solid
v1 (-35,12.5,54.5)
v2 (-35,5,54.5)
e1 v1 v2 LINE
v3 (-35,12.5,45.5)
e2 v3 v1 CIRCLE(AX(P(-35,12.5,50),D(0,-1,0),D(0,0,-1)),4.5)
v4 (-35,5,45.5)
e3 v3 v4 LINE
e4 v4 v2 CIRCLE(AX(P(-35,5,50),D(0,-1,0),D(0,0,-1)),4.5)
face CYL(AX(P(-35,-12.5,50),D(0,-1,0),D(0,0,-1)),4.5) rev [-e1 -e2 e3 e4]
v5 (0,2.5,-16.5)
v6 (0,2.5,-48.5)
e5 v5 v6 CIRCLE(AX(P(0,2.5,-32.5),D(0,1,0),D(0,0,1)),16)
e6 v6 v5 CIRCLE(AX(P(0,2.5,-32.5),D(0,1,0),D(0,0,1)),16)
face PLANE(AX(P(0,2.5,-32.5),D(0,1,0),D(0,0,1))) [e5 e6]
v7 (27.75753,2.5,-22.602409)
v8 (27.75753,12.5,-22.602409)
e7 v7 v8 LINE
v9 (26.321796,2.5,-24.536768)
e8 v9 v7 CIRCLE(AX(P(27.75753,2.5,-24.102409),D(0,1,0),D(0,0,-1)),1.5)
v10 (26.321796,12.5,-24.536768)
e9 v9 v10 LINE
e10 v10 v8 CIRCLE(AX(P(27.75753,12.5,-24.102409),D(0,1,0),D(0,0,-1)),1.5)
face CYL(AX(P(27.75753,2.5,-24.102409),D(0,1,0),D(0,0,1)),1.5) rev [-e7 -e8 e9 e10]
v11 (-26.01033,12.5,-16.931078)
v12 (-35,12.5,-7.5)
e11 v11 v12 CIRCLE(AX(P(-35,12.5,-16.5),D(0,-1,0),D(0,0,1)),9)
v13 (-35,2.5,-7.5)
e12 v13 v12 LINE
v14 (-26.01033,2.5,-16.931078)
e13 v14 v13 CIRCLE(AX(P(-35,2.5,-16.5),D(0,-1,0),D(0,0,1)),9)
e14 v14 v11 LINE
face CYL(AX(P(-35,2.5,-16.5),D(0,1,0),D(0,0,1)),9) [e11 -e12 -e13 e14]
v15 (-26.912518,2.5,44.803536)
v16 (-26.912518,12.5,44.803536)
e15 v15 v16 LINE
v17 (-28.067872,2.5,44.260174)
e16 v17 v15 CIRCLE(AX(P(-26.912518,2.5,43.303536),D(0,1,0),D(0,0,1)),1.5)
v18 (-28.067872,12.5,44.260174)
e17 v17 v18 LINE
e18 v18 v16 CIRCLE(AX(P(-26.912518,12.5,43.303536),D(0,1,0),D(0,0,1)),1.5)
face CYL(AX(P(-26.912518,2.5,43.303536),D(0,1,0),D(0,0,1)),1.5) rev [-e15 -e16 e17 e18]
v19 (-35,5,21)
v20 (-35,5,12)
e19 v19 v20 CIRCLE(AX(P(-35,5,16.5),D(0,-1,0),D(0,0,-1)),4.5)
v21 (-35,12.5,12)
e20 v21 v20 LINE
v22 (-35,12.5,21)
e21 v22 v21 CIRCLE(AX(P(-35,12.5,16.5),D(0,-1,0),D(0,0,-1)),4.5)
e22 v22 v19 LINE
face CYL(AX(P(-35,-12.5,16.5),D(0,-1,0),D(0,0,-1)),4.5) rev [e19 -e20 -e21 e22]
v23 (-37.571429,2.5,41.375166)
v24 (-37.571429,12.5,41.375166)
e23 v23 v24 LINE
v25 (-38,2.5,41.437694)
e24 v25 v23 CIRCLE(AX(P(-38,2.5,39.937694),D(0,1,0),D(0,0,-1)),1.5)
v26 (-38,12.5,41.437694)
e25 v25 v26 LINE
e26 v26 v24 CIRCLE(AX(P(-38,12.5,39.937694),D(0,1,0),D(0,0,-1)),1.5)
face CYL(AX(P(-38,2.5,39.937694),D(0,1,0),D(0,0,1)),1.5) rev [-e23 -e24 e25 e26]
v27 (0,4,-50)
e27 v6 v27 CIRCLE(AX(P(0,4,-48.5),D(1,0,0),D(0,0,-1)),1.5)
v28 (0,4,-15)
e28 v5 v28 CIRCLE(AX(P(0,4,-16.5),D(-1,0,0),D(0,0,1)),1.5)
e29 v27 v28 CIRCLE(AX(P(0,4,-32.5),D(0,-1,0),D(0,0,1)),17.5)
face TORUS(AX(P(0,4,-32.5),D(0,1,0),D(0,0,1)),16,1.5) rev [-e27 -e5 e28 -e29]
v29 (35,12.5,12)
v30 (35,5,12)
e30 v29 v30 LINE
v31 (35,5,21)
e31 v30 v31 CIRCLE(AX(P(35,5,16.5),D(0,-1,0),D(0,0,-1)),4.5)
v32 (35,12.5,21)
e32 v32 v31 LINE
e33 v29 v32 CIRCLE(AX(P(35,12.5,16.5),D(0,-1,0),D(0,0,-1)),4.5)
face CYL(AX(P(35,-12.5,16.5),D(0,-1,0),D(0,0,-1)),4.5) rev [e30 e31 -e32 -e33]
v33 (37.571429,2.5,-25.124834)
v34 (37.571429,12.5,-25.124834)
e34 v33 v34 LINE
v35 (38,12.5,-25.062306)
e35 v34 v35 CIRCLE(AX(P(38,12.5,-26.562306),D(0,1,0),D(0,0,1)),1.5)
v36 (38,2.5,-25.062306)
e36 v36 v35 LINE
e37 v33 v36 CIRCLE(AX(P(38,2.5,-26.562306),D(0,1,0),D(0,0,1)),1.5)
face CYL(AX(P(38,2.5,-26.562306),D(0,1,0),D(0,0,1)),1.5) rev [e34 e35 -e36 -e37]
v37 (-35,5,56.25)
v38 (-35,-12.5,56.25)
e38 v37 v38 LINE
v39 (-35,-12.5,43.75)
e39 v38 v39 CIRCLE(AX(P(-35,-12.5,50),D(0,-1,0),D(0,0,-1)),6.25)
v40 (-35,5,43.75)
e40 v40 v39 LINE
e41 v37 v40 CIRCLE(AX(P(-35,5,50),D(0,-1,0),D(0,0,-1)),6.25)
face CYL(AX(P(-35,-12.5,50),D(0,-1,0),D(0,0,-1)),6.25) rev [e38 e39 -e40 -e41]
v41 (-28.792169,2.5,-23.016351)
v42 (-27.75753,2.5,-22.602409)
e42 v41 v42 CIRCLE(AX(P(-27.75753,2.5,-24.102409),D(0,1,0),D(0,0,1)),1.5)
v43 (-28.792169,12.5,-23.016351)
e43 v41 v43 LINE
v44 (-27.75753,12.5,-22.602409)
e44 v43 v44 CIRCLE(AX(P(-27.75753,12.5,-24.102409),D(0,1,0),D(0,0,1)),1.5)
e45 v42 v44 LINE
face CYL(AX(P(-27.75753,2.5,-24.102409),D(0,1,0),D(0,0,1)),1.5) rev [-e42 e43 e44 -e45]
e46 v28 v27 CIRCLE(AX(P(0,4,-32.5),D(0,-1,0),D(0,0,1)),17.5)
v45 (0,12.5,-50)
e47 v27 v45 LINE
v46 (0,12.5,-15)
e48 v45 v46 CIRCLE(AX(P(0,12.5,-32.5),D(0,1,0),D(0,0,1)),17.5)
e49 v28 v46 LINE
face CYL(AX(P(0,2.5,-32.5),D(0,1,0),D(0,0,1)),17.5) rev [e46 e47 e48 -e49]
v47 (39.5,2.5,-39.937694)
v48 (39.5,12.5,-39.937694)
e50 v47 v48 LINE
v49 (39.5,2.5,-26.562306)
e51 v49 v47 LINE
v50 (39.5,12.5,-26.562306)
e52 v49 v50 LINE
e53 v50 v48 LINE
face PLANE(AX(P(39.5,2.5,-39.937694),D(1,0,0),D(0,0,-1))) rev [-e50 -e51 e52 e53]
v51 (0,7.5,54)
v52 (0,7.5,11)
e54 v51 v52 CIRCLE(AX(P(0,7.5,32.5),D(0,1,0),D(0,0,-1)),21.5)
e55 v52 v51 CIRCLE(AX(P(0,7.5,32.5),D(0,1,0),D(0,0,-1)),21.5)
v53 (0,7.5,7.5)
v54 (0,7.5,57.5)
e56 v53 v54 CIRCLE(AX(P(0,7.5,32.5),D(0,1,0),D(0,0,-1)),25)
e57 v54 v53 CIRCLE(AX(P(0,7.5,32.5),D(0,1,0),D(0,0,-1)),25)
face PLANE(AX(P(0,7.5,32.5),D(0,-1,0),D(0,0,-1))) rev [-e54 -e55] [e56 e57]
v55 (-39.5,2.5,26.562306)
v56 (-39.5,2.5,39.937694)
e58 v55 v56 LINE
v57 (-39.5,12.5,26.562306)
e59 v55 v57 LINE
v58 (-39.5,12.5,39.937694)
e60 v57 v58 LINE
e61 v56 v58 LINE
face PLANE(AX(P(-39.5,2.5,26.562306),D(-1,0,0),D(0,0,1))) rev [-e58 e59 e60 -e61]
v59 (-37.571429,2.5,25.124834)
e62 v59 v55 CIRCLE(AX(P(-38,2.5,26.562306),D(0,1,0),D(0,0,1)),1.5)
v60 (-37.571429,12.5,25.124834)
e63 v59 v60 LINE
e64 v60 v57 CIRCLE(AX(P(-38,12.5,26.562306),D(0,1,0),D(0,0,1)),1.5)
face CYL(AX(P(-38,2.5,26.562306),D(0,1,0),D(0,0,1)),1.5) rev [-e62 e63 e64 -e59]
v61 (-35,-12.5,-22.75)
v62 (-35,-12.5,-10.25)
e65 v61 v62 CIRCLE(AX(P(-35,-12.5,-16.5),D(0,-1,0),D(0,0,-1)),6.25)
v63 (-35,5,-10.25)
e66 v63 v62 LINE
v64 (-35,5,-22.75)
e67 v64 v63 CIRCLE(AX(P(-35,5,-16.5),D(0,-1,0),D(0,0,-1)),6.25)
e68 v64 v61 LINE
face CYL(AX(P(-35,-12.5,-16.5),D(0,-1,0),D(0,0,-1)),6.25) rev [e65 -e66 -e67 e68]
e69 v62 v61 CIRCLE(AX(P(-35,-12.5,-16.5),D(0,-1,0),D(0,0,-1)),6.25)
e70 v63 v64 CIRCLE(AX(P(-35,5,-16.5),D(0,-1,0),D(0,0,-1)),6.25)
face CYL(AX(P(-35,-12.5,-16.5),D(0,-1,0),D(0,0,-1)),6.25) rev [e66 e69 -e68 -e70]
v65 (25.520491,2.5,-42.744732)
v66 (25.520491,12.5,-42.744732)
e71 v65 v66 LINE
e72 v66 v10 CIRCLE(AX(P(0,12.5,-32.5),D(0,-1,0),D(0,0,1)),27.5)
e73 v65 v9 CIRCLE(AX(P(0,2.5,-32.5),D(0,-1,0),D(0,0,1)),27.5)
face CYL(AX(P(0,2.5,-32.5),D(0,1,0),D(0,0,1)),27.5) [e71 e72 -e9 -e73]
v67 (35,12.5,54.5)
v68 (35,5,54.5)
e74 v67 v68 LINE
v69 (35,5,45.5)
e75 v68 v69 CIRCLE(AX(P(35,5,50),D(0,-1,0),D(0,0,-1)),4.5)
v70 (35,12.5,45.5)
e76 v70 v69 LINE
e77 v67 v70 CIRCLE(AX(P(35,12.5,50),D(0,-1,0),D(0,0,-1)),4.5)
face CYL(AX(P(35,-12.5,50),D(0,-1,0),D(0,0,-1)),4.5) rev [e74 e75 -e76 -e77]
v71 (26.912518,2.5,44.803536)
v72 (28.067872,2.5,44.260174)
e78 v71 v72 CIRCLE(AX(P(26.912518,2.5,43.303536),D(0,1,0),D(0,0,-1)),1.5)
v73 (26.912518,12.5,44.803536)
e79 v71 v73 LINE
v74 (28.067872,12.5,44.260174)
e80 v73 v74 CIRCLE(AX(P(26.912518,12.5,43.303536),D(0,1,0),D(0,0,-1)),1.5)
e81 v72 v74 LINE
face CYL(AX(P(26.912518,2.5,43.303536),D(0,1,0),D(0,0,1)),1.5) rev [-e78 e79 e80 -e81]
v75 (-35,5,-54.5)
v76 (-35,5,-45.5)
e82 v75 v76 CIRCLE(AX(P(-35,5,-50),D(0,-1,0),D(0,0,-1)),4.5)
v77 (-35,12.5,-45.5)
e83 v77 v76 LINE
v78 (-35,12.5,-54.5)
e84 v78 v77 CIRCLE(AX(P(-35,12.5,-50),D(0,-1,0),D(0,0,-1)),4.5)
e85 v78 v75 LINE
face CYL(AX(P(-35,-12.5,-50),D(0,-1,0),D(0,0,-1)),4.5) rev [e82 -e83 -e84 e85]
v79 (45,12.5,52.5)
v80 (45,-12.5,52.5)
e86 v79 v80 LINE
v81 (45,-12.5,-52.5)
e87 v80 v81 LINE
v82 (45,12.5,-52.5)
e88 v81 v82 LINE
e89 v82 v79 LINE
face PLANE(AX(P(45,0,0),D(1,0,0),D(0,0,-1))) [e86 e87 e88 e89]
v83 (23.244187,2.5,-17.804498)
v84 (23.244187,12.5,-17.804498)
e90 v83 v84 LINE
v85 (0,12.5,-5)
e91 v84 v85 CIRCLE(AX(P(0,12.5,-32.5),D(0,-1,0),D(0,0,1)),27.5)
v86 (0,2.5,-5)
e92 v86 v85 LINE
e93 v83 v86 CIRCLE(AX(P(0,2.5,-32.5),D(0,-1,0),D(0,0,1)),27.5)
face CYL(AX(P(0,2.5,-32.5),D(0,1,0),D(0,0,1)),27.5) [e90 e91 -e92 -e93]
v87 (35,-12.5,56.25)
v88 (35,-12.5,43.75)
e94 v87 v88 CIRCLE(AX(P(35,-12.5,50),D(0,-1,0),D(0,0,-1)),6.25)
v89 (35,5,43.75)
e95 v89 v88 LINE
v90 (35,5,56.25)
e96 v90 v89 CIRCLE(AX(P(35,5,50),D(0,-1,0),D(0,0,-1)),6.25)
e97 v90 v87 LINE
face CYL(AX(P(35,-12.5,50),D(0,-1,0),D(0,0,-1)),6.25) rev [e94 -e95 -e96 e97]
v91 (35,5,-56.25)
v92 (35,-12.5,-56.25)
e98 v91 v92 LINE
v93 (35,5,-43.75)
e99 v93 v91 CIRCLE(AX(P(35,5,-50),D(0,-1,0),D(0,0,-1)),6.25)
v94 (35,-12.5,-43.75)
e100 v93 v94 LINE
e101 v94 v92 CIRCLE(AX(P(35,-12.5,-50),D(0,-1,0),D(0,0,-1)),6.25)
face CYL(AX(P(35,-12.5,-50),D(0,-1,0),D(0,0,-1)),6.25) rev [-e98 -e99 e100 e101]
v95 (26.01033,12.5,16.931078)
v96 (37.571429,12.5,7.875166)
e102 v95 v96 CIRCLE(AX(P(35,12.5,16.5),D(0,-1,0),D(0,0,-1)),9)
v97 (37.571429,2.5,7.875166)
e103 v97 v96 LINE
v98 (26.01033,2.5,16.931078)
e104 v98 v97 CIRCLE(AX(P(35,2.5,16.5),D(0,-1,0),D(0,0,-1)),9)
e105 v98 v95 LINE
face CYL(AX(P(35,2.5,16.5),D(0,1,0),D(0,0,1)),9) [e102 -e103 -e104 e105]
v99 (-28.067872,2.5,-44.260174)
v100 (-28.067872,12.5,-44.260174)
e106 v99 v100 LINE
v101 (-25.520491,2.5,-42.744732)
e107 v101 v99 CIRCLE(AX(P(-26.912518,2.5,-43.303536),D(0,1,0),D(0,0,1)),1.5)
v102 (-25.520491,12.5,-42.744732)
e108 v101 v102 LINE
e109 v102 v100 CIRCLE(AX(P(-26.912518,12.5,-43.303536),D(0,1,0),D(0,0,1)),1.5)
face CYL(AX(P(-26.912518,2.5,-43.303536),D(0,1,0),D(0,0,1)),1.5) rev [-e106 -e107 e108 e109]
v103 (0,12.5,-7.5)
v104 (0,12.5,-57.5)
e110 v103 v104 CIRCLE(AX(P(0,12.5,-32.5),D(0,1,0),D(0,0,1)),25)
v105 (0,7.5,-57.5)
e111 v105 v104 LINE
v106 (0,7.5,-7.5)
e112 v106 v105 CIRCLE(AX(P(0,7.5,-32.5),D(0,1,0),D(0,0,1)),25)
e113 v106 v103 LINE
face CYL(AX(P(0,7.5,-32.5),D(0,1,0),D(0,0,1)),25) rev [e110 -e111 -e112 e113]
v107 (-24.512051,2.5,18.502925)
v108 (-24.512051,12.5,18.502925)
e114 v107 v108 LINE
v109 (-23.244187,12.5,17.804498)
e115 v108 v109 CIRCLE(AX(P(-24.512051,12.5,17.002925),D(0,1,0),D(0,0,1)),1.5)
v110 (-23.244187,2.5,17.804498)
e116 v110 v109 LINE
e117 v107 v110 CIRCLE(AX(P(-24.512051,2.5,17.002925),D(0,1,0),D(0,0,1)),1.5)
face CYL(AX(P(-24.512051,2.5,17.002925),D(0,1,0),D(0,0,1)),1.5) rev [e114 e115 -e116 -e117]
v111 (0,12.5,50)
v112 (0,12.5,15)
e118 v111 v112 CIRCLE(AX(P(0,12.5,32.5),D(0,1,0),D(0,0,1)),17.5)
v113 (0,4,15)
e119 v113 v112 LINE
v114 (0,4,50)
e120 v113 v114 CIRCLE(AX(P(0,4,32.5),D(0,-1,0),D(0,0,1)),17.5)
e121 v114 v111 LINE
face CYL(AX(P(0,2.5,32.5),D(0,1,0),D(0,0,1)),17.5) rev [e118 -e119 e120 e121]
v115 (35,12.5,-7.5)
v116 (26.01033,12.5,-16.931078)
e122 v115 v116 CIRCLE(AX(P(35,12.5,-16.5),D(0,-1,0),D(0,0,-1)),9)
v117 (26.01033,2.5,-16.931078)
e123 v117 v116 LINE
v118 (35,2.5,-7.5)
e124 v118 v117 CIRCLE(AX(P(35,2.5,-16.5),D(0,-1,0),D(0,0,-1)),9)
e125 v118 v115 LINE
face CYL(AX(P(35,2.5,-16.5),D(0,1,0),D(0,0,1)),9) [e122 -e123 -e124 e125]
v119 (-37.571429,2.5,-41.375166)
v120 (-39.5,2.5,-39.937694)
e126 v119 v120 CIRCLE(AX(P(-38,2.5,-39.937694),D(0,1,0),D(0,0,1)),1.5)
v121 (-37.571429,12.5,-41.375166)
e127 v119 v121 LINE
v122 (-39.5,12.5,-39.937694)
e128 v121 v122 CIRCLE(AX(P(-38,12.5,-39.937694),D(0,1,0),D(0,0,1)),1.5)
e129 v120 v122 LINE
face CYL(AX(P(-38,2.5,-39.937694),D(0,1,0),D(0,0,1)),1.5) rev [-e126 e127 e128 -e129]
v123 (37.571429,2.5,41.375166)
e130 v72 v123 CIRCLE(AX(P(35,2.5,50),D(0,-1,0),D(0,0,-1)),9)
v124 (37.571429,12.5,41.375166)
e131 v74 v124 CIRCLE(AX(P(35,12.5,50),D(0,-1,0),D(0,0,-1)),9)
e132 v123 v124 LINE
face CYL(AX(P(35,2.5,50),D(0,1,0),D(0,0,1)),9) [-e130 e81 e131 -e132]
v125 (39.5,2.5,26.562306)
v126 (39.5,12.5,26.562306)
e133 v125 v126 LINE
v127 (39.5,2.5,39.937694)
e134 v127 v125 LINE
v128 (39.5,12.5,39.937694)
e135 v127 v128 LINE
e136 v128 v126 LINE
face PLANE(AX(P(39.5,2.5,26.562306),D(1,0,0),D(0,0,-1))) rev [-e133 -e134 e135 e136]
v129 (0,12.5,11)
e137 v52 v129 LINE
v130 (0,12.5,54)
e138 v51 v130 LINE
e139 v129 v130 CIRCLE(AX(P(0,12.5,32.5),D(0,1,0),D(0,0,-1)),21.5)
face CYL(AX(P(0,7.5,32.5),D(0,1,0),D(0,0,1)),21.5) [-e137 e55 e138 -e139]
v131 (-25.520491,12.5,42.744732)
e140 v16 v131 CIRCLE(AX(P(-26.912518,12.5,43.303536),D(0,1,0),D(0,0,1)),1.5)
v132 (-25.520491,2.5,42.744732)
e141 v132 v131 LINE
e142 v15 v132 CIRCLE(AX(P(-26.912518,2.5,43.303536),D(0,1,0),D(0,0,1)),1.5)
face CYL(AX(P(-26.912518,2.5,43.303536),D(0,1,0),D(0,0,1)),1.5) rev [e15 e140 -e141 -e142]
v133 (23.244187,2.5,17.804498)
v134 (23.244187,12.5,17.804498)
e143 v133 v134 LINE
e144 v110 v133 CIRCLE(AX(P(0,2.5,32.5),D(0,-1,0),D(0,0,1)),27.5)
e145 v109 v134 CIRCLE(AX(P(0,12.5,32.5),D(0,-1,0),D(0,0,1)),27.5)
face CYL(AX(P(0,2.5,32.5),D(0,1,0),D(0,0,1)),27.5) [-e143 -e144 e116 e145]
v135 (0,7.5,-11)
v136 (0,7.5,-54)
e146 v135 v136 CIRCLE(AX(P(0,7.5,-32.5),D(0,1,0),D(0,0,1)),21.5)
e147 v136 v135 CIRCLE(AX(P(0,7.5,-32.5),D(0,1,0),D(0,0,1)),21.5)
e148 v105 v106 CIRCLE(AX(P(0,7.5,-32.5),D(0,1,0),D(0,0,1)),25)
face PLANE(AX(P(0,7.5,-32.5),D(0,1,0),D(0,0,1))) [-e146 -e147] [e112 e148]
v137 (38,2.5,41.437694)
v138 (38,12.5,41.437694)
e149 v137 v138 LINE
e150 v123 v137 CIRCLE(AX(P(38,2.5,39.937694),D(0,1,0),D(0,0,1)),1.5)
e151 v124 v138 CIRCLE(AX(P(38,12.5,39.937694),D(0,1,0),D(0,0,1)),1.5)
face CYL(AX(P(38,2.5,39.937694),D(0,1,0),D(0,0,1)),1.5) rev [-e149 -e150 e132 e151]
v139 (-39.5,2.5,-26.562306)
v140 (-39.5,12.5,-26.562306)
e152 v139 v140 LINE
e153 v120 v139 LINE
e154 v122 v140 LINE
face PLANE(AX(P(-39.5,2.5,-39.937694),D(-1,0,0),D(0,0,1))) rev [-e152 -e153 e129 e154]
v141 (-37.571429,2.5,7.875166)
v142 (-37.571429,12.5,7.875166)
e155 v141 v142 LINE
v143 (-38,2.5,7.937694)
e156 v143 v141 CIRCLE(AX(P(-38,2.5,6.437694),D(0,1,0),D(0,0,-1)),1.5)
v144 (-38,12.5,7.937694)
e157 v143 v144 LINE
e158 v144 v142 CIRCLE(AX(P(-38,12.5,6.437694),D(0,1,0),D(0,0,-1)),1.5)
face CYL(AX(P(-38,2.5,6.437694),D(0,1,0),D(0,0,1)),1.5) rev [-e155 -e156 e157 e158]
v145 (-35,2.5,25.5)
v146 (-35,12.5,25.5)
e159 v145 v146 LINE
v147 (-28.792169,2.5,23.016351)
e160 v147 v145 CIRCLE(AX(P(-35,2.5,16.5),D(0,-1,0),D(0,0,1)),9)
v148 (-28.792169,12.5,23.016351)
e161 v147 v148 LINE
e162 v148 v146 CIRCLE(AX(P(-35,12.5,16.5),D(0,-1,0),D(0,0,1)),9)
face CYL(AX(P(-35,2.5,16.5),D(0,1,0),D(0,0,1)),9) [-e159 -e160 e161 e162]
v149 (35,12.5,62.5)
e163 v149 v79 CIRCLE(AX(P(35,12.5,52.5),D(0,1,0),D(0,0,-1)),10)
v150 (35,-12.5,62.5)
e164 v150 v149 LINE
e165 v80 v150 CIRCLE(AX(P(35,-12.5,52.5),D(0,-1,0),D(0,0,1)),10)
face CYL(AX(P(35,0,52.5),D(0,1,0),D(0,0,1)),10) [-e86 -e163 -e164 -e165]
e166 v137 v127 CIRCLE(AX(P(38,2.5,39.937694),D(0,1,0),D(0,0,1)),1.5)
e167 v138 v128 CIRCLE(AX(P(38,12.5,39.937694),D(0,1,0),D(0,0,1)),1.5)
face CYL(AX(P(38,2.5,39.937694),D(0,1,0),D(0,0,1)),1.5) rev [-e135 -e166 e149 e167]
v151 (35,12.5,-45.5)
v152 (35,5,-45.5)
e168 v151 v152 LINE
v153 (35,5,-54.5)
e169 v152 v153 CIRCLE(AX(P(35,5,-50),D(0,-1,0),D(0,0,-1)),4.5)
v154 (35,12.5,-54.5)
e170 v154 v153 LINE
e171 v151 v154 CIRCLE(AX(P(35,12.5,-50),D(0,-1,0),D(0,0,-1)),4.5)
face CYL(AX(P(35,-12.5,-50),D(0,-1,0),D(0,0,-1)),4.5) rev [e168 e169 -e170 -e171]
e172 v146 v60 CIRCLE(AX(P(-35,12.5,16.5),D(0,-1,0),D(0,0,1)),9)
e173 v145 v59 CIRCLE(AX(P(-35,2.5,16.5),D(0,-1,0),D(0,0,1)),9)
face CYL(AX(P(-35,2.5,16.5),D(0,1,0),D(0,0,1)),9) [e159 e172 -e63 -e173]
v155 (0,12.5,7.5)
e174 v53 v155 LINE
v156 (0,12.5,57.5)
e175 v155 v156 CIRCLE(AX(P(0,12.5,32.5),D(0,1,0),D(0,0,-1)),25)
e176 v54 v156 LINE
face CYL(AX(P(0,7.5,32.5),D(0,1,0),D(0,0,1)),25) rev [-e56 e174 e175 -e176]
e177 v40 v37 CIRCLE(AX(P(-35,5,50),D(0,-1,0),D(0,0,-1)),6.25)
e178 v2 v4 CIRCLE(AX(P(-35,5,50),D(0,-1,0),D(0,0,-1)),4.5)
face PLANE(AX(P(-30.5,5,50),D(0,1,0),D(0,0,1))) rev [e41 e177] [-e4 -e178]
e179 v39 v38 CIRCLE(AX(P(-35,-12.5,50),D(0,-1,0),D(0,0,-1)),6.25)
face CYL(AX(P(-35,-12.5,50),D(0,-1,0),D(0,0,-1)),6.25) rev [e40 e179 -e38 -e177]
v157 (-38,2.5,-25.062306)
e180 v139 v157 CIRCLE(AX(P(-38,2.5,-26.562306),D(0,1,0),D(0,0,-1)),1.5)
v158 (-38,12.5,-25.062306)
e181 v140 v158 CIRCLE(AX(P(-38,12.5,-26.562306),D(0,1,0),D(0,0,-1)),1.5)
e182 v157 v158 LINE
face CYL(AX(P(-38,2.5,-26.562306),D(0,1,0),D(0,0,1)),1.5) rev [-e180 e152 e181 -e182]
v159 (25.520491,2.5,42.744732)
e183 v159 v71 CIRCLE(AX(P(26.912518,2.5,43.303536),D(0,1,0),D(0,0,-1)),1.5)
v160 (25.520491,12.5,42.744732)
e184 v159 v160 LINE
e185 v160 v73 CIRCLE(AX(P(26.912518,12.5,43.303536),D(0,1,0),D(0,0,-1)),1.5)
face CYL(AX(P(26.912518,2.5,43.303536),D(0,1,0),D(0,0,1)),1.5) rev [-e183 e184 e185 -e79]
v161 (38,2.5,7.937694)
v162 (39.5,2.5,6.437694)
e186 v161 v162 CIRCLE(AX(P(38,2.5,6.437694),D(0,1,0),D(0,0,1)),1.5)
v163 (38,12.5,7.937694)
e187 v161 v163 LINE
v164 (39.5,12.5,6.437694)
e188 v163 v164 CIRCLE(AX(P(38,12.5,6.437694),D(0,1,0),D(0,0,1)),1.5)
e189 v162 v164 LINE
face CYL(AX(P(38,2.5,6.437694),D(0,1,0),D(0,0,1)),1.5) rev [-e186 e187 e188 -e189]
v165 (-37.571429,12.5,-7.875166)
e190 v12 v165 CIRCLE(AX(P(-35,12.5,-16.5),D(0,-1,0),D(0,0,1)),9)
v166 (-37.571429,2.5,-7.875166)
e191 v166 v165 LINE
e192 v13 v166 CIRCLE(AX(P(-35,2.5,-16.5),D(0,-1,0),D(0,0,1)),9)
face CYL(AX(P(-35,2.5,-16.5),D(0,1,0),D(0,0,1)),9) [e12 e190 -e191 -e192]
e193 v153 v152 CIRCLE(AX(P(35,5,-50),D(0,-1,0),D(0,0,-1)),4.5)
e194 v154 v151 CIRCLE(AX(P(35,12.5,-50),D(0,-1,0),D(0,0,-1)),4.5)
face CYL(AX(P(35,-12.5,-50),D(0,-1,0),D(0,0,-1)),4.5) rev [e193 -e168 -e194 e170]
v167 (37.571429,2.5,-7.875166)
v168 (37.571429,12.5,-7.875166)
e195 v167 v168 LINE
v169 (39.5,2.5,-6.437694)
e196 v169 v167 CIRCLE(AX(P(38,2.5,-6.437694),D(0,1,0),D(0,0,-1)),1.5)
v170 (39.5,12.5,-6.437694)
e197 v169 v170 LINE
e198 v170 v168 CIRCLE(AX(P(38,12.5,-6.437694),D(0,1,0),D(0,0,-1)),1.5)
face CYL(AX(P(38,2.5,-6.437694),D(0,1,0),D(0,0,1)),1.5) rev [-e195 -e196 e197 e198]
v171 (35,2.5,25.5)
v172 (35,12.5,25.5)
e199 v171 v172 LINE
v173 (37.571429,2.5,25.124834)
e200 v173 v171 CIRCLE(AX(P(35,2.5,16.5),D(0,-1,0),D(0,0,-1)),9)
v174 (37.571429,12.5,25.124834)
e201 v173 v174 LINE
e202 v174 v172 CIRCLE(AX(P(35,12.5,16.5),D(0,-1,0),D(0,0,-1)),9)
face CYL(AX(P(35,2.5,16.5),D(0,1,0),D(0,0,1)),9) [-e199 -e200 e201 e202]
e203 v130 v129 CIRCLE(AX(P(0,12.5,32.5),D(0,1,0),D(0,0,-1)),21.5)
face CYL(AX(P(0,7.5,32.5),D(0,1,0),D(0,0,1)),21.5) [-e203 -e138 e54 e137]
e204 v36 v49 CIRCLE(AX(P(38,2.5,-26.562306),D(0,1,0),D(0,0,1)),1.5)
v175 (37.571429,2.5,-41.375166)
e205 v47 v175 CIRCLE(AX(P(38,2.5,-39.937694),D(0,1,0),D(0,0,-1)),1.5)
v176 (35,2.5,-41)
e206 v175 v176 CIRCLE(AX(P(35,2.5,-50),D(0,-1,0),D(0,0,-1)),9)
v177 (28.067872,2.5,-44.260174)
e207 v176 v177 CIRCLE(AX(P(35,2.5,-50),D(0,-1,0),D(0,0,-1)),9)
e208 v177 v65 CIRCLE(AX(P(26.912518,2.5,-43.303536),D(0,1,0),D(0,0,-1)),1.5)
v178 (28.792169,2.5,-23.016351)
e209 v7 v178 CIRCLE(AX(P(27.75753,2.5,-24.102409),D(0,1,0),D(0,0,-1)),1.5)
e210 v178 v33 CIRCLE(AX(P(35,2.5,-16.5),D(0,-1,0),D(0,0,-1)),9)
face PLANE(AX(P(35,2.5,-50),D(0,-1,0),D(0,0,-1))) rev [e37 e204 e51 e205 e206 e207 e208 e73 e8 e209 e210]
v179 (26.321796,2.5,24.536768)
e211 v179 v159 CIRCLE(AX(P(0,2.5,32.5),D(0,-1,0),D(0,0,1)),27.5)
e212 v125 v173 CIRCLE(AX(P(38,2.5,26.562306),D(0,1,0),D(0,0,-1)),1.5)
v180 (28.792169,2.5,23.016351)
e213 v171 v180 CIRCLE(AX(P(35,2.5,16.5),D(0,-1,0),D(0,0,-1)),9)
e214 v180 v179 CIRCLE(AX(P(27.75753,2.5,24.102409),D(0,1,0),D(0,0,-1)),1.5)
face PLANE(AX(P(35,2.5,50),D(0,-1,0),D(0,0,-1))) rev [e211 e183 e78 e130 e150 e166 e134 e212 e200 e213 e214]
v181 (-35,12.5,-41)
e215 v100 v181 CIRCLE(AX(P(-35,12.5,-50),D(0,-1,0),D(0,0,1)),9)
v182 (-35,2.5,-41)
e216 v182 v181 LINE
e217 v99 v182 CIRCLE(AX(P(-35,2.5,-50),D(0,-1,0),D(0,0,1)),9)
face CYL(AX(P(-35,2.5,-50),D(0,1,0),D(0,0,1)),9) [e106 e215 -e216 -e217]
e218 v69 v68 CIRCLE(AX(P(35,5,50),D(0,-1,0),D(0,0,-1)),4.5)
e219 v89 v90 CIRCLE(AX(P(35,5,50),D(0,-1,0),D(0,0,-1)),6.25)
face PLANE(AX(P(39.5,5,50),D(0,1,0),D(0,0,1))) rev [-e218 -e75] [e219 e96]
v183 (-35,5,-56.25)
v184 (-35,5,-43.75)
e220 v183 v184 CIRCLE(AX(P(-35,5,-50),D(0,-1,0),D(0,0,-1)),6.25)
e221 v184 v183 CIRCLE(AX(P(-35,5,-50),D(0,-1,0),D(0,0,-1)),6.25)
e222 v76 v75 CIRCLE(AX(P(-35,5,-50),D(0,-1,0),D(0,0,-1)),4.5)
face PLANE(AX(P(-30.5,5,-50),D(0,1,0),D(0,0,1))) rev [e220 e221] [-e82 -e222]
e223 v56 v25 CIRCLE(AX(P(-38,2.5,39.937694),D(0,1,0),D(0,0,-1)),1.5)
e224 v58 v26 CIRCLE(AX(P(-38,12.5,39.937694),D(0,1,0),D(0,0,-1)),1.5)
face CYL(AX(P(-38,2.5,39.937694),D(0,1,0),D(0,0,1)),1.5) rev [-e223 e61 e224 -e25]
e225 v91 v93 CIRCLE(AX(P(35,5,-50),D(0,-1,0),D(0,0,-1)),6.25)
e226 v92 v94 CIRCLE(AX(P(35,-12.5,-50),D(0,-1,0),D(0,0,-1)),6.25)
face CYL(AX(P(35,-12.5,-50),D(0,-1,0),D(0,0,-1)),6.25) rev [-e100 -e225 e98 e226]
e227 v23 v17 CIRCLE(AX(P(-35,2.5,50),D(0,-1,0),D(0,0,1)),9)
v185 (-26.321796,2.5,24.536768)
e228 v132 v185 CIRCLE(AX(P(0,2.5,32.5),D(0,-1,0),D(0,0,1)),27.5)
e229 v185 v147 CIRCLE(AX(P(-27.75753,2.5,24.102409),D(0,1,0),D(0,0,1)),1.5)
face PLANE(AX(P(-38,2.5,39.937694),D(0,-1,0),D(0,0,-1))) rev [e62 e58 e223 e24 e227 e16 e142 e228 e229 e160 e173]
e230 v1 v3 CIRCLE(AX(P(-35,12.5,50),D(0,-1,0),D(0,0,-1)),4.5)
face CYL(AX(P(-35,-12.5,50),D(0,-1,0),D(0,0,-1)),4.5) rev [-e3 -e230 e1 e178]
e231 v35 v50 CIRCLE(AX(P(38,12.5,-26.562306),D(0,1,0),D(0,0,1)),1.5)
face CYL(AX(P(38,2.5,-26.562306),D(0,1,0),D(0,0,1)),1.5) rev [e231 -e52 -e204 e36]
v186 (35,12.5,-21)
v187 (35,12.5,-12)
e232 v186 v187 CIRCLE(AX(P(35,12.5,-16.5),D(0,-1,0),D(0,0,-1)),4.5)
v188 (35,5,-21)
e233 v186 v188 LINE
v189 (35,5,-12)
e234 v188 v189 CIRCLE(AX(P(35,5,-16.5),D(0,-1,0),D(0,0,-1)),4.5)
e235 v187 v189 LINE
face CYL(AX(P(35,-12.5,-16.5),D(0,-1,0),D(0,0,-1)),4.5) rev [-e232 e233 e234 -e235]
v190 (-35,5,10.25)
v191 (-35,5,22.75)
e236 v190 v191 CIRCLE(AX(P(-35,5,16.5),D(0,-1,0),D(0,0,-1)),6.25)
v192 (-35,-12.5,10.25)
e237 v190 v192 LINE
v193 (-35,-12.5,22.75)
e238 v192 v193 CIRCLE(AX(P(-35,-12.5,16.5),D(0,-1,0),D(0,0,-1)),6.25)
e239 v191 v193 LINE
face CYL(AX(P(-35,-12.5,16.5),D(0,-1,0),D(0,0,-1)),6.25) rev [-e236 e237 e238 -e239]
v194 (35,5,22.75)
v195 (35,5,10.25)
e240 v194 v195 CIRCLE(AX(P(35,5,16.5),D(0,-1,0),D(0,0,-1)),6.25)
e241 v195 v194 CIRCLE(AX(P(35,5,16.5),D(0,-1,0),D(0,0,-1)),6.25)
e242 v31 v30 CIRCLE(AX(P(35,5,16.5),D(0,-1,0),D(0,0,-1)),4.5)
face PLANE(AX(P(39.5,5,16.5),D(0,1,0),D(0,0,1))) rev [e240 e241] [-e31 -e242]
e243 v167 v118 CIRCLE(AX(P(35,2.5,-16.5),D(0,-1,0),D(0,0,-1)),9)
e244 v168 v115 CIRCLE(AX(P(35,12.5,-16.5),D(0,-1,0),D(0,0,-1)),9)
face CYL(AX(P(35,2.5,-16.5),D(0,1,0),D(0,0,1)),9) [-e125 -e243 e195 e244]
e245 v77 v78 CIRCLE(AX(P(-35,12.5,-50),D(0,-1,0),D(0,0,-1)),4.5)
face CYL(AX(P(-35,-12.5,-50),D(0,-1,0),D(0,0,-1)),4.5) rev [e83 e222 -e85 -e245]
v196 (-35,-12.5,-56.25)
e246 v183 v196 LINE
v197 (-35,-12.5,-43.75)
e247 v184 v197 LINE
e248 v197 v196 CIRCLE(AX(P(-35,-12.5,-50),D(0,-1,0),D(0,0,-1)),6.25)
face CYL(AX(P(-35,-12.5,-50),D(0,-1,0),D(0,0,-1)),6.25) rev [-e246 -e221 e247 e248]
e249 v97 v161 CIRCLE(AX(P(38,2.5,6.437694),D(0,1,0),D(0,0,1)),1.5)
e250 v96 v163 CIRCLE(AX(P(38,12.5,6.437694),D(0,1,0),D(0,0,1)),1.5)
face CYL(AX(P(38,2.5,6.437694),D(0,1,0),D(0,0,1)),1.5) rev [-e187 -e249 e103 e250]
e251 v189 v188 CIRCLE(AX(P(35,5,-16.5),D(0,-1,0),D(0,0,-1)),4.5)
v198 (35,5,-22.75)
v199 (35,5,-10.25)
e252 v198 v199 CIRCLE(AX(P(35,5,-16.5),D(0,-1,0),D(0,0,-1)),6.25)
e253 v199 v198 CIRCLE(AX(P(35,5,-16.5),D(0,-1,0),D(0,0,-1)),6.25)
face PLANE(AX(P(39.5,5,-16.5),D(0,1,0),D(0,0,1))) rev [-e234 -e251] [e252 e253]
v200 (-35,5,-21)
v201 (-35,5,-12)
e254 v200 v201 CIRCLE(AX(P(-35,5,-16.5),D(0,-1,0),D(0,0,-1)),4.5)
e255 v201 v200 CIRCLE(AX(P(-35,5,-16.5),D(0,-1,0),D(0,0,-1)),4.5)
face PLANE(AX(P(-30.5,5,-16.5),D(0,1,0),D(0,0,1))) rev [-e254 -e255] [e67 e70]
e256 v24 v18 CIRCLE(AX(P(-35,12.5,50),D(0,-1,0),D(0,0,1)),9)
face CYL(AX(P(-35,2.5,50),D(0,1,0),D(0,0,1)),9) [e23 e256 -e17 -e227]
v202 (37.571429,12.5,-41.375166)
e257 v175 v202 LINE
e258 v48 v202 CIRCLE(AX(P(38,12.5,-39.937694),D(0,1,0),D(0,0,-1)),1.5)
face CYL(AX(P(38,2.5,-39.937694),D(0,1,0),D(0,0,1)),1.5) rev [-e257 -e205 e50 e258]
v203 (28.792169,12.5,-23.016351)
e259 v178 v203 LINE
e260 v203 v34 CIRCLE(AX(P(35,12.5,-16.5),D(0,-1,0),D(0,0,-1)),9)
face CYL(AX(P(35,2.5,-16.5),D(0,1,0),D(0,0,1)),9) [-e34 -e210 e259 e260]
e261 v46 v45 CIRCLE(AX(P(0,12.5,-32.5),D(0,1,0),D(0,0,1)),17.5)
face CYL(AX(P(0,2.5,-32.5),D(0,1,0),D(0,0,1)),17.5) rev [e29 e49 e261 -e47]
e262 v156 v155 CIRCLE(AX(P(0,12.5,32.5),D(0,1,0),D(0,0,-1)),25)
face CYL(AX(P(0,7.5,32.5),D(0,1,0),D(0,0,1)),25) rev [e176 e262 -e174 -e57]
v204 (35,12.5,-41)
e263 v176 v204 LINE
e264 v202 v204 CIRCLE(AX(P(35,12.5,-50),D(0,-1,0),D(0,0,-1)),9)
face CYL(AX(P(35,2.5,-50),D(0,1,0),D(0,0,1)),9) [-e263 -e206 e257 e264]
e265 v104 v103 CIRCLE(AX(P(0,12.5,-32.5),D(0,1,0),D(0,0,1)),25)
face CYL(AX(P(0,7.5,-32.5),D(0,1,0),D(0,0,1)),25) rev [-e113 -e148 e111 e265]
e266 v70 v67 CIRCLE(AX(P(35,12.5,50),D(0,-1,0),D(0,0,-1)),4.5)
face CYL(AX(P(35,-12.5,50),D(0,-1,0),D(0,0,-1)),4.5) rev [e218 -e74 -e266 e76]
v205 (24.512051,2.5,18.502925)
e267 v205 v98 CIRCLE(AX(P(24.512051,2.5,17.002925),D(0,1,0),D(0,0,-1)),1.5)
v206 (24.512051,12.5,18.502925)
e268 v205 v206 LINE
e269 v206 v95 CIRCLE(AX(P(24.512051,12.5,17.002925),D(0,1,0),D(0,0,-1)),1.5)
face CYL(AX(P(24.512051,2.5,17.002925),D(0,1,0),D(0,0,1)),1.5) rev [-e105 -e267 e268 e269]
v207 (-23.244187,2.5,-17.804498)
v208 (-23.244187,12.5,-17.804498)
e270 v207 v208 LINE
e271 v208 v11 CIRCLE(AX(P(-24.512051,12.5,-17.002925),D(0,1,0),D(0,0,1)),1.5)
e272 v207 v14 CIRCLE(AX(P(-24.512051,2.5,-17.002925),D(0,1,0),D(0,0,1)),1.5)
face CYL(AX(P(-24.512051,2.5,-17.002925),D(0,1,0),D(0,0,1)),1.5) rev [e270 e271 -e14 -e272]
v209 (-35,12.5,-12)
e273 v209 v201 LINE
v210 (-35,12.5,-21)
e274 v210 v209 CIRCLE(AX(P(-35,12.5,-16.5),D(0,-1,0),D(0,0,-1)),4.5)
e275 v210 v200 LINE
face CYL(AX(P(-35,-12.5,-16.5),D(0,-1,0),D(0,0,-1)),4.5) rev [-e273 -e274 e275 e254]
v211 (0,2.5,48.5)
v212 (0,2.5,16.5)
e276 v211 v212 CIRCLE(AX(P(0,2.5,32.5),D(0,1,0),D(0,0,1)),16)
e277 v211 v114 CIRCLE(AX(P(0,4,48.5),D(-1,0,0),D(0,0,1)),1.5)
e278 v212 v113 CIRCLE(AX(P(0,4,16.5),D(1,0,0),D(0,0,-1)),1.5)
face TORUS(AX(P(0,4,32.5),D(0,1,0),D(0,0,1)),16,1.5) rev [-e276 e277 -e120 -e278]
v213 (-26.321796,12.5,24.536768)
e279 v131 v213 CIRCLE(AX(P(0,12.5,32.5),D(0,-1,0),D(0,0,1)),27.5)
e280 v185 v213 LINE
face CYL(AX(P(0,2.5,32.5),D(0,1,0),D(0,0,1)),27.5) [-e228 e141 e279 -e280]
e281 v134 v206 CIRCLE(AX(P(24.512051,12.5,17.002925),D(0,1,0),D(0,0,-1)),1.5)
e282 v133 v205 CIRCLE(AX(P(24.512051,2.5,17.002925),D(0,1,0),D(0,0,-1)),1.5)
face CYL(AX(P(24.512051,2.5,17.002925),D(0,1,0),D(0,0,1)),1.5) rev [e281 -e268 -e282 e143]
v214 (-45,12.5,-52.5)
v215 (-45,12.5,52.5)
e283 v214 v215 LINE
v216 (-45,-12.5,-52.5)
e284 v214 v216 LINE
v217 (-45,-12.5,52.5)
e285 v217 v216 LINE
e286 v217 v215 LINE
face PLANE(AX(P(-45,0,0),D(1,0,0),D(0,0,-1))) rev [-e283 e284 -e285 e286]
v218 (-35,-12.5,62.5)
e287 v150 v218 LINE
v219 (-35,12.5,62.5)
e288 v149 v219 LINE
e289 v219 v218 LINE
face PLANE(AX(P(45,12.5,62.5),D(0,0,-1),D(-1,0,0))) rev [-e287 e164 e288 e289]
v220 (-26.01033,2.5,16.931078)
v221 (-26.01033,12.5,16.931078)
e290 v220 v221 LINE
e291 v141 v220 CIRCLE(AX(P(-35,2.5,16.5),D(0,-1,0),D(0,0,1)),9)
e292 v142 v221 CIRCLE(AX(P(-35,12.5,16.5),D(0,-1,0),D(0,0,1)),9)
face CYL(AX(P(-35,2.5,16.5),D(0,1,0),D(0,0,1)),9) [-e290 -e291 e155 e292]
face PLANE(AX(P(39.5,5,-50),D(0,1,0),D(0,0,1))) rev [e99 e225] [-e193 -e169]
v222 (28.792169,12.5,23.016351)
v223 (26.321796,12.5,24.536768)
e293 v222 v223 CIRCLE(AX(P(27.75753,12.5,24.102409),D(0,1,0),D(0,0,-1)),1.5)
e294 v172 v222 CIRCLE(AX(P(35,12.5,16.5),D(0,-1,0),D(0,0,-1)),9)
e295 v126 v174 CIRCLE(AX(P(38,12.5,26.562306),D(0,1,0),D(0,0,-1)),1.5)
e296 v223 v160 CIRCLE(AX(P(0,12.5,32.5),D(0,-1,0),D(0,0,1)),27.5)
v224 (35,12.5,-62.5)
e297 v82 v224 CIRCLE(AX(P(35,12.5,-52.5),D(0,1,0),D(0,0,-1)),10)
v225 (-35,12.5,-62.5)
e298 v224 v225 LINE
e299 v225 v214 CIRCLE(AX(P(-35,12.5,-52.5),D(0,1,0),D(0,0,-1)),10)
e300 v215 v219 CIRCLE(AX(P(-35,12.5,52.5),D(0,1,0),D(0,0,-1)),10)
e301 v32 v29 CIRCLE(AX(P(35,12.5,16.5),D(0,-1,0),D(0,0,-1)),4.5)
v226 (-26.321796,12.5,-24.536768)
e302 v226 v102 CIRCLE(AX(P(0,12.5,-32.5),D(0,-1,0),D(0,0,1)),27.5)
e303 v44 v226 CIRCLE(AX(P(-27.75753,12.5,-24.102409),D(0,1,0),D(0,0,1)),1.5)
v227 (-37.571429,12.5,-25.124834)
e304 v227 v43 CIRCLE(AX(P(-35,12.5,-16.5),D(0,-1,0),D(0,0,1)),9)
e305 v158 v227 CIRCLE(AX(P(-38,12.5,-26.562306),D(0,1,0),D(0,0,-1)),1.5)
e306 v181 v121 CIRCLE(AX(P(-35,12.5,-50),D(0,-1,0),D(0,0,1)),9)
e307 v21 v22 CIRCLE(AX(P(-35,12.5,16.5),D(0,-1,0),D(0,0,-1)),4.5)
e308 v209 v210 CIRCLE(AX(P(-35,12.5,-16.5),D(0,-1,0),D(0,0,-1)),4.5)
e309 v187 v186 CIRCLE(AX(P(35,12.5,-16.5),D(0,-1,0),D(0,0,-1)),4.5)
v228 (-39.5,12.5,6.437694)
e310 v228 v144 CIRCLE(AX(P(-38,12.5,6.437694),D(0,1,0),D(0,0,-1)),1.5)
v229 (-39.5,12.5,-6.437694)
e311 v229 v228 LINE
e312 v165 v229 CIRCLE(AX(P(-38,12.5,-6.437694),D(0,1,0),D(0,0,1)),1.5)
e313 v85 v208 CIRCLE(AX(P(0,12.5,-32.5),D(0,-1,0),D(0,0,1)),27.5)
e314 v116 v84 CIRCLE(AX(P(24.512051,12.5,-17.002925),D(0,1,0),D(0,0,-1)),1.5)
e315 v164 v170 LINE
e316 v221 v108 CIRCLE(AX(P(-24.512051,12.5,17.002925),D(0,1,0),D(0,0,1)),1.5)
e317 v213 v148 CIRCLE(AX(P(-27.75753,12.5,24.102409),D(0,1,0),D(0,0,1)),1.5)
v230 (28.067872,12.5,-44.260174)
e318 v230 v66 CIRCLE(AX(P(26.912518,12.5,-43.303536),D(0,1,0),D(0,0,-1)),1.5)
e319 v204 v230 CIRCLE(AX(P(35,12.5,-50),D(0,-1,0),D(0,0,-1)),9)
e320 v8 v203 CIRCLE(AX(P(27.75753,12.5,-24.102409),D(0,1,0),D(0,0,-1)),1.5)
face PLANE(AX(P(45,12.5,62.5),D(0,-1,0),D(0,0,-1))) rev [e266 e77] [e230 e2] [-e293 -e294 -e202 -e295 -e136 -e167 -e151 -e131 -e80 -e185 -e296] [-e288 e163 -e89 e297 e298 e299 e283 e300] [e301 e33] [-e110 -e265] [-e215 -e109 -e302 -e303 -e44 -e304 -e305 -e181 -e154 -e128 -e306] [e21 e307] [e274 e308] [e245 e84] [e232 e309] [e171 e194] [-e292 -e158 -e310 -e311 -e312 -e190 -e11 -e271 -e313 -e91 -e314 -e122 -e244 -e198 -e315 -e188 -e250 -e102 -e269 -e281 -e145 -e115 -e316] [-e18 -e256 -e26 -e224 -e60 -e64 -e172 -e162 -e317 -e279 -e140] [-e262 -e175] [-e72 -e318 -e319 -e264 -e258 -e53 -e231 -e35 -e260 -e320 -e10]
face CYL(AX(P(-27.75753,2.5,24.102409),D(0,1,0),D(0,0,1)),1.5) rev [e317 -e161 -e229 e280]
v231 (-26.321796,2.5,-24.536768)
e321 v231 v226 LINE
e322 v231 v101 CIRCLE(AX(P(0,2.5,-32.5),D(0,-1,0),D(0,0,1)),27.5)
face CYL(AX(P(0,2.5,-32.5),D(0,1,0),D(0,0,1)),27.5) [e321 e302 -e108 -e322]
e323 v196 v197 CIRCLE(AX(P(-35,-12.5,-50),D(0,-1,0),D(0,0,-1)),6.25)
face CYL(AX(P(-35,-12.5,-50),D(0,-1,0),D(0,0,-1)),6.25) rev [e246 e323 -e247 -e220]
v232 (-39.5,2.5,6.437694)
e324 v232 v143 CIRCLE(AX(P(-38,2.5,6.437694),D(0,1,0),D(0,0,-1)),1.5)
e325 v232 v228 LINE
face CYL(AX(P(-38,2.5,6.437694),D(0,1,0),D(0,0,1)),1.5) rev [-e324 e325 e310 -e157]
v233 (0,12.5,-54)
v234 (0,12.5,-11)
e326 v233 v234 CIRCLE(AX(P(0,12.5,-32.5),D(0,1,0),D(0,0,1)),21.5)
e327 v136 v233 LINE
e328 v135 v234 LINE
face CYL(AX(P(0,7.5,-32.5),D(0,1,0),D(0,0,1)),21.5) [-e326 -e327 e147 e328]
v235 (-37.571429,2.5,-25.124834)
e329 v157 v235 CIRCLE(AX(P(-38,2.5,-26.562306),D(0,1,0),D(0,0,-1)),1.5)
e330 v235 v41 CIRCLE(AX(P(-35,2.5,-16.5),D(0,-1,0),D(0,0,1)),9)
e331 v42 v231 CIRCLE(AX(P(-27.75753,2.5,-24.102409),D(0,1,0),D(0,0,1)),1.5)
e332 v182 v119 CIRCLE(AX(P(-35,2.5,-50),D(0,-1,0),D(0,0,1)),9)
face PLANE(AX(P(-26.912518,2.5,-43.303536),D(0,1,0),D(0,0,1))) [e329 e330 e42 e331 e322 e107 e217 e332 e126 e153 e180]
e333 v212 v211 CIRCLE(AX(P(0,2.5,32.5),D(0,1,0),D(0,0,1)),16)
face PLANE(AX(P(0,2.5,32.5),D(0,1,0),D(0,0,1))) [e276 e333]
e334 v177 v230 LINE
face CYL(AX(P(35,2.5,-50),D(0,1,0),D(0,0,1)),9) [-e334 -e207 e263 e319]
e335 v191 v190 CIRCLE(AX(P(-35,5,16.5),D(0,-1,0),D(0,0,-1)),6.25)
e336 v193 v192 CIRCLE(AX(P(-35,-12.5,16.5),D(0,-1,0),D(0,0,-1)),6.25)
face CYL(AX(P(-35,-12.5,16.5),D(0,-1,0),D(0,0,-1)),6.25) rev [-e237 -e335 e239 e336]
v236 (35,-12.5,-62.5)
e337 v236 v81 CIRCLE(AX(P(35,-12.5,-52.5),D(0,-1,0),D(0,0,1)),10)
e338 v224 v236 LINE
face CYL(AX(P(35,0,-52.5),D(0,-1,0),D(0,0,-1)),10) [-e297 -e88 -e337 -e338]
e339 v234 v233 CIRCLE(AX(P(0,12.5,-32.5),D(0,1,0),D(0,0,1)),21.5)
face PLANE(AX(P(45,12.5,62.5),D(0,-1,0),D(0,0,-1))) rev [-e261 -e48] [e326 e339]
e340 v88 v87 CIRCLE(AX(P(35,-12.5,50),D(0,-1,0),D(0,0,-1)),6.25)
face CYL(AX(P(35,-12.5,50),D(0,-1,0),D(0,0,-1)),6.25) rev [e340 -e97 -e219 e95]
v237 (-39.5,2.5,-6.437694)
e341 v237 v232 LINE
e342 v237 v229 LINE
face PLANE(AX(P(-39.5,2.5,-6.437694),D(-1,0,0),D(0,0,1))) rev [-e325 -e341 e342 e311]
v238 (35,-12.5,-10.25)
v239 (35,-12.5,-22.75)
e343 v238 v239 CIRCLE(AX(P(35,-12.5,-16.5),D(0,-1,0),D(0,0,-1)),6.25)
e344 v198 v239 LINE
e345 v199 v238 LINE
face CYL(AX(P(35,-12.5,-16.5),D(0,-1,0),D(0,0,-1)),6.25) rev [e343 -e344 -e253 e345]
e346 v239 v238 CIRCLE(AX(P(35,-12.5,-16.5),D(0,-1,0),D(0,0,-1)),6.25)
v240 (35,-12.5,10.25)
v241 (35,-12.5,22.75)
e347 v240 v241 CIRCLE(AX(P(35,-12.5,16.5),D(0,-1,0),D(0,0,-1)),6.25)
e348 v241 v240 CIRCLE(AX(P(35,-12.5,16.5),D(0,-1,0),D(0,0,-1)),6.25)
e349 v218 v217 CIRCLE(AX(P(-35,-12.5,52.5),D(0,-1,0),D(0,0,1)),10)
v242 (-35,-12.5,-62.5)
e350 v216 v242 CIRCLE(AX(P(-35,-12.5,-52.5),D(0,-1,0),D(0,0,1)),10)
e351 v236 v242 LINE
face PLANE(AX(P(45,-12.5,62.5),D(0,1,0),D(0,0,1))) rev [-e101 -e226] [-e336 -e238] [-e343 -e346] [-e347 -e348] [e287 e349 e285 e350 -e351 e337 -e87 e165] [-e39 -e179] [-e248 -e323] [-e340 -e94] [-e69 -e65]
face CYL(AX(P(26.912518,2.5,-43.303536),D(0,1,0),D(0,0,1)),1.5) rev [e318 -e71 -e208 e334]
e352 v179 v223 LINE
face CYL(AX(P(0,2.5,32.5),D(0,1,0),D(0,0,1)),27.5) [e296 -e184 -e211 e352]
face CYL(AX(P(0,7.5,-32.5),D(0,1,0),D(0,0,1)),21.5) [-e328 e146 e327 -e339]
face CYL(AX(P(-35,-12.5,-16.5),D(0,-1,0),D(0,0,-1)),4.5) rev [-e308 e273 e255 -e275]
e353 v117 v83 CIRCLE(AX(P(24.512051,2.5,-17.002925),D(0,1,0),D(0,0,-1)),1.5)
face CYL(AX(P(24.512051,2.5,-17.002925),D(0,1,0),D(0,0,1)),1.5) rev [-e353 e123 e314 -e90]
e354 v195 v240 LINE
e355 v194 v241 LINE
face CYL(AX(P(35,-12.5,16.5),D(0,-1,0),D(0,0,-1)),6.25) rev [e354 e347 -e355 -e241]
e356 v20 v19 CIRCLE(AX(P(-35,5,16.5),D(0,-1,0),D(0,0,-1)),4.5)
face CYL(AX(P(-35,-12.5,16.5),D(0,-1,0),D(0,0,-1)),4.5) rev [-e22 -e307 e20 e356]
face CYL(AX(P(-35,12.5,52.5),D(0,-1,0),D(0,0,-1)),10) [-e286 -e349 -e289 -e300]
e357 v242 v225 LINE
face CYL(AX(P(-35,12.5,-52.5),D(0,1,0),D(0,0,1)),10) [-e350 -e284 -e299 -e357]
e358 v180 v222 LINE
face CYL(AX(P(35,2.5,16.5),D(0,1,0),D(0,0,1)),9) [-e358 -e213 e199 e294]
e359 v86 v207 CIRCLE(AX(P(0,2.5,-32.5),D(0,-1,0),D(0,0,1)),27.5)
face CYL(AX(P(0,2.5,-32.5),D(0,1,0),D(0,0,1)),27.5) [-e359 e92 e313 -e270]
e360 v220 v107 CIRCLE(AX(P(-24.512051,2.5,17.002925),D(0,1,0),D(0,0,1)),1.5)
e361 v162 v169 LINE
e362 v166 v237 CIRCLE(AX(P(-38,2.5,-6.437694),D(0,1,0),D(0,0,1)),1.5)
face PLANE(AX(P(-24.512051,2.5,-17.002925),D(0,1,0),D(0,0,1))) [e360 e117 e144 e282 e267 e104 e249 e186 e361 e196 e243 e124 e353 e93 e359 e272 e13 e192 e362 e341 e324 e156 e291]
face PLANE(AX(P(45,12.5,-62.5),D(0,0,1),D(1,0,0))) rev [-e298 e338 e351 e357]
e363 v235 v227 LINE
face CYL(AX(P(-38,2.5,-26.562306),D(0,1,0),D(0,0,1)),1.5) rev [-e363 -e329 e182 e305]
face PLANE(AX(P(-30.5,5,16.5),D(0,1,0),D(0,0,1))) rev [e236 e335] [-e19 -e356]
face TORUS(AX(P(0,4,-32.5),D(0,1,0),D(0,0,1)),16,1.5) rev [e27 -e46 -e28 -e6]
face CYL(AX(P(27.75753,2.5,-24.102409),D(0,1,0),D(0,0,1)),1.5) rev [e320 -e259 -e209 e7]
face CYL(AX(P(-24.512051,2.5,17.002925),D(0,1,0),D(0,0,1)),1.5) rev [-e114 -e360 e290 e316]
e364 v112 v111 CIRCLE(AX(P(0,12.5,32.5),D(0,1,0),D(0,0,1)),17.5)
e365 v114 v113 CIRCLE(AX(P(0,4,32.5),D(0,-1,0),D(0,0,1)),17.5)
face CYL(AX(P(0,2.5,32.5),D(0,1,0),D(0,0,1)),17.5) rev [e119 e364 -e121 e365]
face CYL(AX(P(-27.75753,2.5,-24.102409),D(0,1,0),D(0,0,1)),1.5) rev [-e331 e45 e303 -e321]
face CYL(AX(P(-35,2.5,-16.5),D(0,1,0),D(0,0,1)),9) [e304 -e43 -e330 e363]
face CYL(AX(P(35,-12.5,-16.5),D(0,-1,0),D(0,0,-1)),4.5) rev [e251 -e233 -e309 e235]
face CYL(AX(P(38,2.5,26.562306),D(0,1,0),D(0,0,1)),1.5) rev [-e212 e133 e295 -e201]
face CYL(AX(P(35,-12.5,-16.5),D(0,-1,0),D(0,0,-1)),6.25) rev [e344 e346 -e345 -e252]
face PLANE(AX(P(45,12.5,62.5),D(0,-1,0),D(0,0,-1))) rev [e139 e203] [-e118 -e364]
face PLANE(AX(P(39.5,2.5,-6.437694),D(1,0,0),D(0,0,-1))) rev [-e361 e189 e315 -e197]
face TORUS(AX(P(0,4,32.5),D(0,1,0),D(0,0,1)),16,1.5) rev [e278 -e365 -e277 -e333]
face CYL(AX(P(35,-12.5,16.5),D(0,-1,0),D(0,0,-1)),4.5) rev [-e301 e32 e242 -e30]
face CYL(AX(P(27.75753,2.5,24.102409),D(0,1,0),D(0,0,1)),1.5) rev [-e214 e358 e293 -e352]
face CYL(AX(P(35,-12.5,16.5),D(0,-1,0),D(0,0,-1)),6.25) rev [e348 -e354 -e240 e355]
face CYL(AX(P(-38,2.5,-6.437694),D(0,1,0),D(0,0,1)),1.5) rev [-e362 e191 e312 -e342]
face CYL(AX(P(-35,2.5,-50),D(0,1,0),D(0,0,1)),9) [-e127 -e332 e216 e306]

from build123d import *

# Parameters (mm, degrees)
BLOCK_PROFILE_SKETCH_W         = 125
BLOCK_PROFILE_SKETCH_H         = 25
BASE_BLOCK_DEPTH               = 45
BORE_RECESS_SKETCH_R           = 25
BORE_RECESS_SKETCH_R_2         = 21.5
BORE_RECESS_5MM_DEPTH          = 5
TWIN_BORE_SKETCH_R             = 17.5
TWIN_BORES_DEPTH               = 10
BORE_EDGE_FILLET_R1_5_R        = 1.5
RELIEF_POCKETS_DEPTH           = 10
BOLT_HOLES_CBORE_9_D           = 9
BOLT_HOLES_CBORE_9_DEPTH       = 100
BOLT_HOLES_CBORE_9_CBORE_D     = 12.5
BOLT_HOLES_CBORE_9_CBORE_DEPTH = 17.5
CORNER_FILLETS_R10_R           = 10


with BuildPart() as part:
    # Block Profile Sketch → Base Block (new, symmetric)
    with BuildSketch(Plane(origin=(0, 0, 0), x_dir=(0, 0, -1), z_dir=(1, 0, 0))):
        Rectangle(BLOCK_PROFILE_SKETCH_W, BLOCK_PROFILE_SKETCH_H)
    extrude(amount=BASE_BLOCK_DEPTH, both=True)

    # Bore Recess Sketch → Bore Recess 5mm (cut)
    # profile 1 of 2: a face of its own
    with BuildSketch(Plane(origin=(0, 12.5, 0), x_dir=(1, 0, 0), z_dir=(0, 1, 0))):
        with Locations(Location((0, 32.5, 0), (0, 0, 270))):
            Circle(BORE_RECESS_SKETCH_R)
        with Locations(Location((0, 32.5, 0), (0, 0, 270))):
            Circle(BORE_RECESS_SKETCH_R_2, mode=Mode.SUBTRACT)
    # profile 2 of 2: a face of its own
    with BuildSketch(Plane(origin=(0, 12.5, 0), x_dir=(1, 0, 0), z_dir=(0, 1, 0))):
        with Locations(Location((0, -32.5, 0), (0, 0, 90))):
            Circle(BORE_RECESS_SKETCH_R)
        with Locations(Location((0, -32.5, 0), (0, 0, 90))):
            Circle(BORE_RECESS_SKETCH_R_2, mode=Mode.SUBTRACT)
    extrude(amount=-BORE_RECESS_5MM_DEPTH, mode=Mode.SUBTRACT)

    # Twin Bore Sketch → Twin Bores (cut)
    with BuildSketch(Plane(origin=(0, 12.5, 0), x_dir=(1, 0, 0), z_dir=(0, 1, 0))):
        with Locations(Location((0, 32.5, 0), (0, 0, 270))):
            Circle(TWIN_BORE_SKETCH_R)
        with Locations(Location((0, -32.5, 0), (0, 0, 270))):
            Circle(TWIN_BORE_SKETCH_R)
    extrude(amount=-TWIN_BORES_DEPTH, mode=Mode.SUBTRACT)

    # Bore Edge Fillet R1.5
    bore_edge_fillet_r1_5_edges = [part.edges().sort_by_distance(p)[0] for p in [
        (0, 2.5, -50),
        (0, 2.5, 15),
    ]]
    fillet(bore_edge_fillet_r1_5_edges, radius=BORE_EDGE_FILLET_R1_5_R)

    # Relief Pocket Sketch → Relief Pockets (cut)
    with BuildSketch(Plane(origin=(0, 12.5, 0), x_dir=(1, 0, 0), z_dir=(0, 1, 0))):
        with BuildLine():
            Line((-39.5, 6.437694101), (-39.5, -6.437694101))
            ThreePointArc((-39.5, -6.437694101), (-38.896421457, -7.64036969), (-37.571428571, -7.875166373))
            ThreePointArc((-37.571428571, -7.875166373), (-29.450149328, -9.41486362), (-26.010329741, -16.931078451))
            ThreePointArc((-26.010329741, -16.931078451), (-24.963701576, -18.433313648), (-23.244186639, -17.804497711))
            ThreePointArc((-23.244186639, -17.804497711), (0, -5), (23.244186639, -17.804497711))
            ThreePointArc((23.244186639, -17.804497711), (24.963701576, -18.433313648), (26.010329741, -16.931078451))
            ThreePointArc((26.010329741, -16.931078451), (29.450149328, -9.41486362), (37.571428571, -7.875166373))
            ThreePointArc((37.571428571, -7.875166373), (38.896421457, -7.64036969), (39.5, -6.437694101))
            Line((39.5, -6.437694101), (39.5, 6.437694101))
            ThreePointArc((39.5, 6.437694101), (38.896421457, 7.64036969), (37.571428571, 7.875166373))
            ThreePointArc((37.571428571, 7.875166373), (29.450149328, 9.41486362), (26.010329741, 16.931078451))
            ThreePointArc((26.010329741, 16.931078451), (24.963701576, 18.433313648), (23.244186639, 17.804497711))
            ThreePointArc((23.244186639, 17.804497711), (0, 5), (-23.244186639, 17.804497711))
            ThreePointArc((-23.244186639, 17.804497711), (-24.963701576, 18.433313648), (-26.010329741, 16.931078451))
            ThreePointArc((-26.010329741, 16.931078451), (-29.450149328, 9.41486362), (-37.571428571, 7.875166373))
            ThreePointArc((-37.571428571, 7.875166373), (-38.896421457, 7.64036969), (-39.5, 6.437694101))
        make_face()
        with BuildLine():
            Line((-39.5, -26.562305899), (-39.5, -39.937694101))
            ThreePointArc((-39.5, -39.937694101), (-38.896421457, -41.14036969), (-37.571428571, -41.375166373))
            ThreePointArc((-37.571428571, -41.375166373), (-32.385666254, -41.388074602), (-28.067872341, -44.260173686))
            ThreePointArc((-28.067872341, -44.260173686), (-26.145612251, -44.5926659), (-25.520490952, -42.744732383))
            ThreePointArc((-25.520490952, -42.744732383), (-27.473408366, -33.709062761), (-26.321795689, -24.53676751))
            ThreePointArc((-26.321795689, -24.53676751), (-26.971313668, -22.824965098), (-28.792168571, -23.016350892))
            ThreePointArc((-28.792168571, -23.016350892), (-32.898267073, -25.251155278), (-37.571428571, -25.124833627))
            ThreePointArc((-37.571428571, -25.124833627), (-38.896421457, -25.35963031), (-39.5, -26.562305899))
        make_face()
        with BuildLine():
            Line((-39.5, 39.937694101), (-39.5, 26.562305899))
            ThreePointArc((-39.5, 26.562305899), (-38.896421457, 25.35963031), (-37.571428571, 25.124833627))
            ThreePointArc((-37.571428571, 25.124833627), (-32.898267073, 25.251155278), (-28.792168571, 23.016350892))
            ThreePointArc((-28.792168571, 23.016350892), (-26.971313668, 22.824965098), (-26.321795689, 24.53676751))
            ThreePointArc((-26.321795689, 24.53676751), (-27.473408366, 33.709062761), (-25.520490952, 42.744732383))
            ThreePointArc((-25.520490952, 42.744732383), (-26.145612251, 44.5926659), (-28.067872341, 44.260173686))
            ThreePointArc((-28.067872341, 44.260173686), (-32.385666254, 41.388074602), (-37.571428571, 41.375166373))
            ThreePointArc((-37.571428571, 41.375166373), (-38.896421457, 41.14036969), (-39.5, 39.937694101))
        make_face()
        with BuildLine():
            Line((39.5, -26.562305899), (39.5, -39.937694101))
            ThreePointArc((39.5, -39.937694101), (38.896421457, -41.14036969), (37.571428571, -41.375166373))
            ThreePointArc((37.571428571, -41.375166373), (32.385666254, -41.388074602), (28.067872341, -44.260173686))
            ThreePointArc((28.067872341, -44.260173686), (26.145612251, -44.5926659), (25.520490952, -42.744732383))
            ThreePointArc((25.520490952, -42.744732383), (27.473408366, -33.709062761), (26.321795689, -24.53676751))
            ThreePointArc((26.321795689, -24.53676751), (26.971313668, -22.824965098), (28.792168571, -23.016350892))
            ThreePointArc((28.792168571, -23.016350892), (32.898267073, -25.251155278), (37.571428571, -25.124833627))
            ThreePointArc((37.571428571, -25.124833627), (38.896421457, -25.35963031), (39.5, -26.562305899))
        make_face()
        with BuildLine():
            Line((39.5, 39.937694101), (39.5, 26.562305899))
            ThreePointArc((39.5, 26.562305899), (38.896421457, 25.35963031), (37.571428571, 25.124833627))
            ThreePointArc((37.571428571, 25.124833627), (32.898267073, 25.251155278), (28.792168571, 23.016350892))
            ThreePointArc((28.792168571, 23.016350892), (26.971313668, 22.824965098), (26.321795689, 24.53676751))
            ThreePointArc((26.321795689, 24.53676751), (27.473408366, 33.709062761), (25.520490952, 42.744732383))
            ThreePointArc((25.520490952, 42.744732383), (26.145612251, 44.5926659), (28.067872341, 44.260173686))
            ThreePointArc((28.067872341, 44.260173686), (32.385666254, 41.388074602), (37.571428571, 41.375166373))
            ThreePointArc((37.571428571, 41.375166373), (38.896421457, 41.14036969), (39.5, 39.937694101))
        make_face()
    extrude(amount=-RELIEF_POCKETS_DEPTH, mode=Mode.SUBTRACT)

    # Bolt Holes CBore Ø9
    with Locations(Plane(origin=(0, -12.5, 0), x_dir=(-1, 0, 0), z_dir=(0, -1, 0))):
        with Locations((-35, -50), (35, -50), (-35, -16.5), (-35, 16.5), (-35, 50), (35, 50), (35, 16.5), (35, -16.5)):
            CounterBoreHole(BOLT_HOLES_CBORE_9_D / 2, BOLT_HOLES_CBORE_9_CBORE_D / 2, BOLT_HOLES_CBORE_9_CBORE_DEPTH, depth=BOLT_HOLES_CBORE_9_DEPTH)

    # Corner Fillets R10
    corner_fillets_r10_edges = [part.edges().sort_by_distance(p)[0] for p in [
        (45, 0, 62.5),
        (45, 0, -62.5),
        (-45, 0, 62.5),
        (-45, 0, -62.5),
    ]]
    fillet(corner_fillets_r10_edges, radius=CORNER_FILLETS_R10_R)


solid = part.part
